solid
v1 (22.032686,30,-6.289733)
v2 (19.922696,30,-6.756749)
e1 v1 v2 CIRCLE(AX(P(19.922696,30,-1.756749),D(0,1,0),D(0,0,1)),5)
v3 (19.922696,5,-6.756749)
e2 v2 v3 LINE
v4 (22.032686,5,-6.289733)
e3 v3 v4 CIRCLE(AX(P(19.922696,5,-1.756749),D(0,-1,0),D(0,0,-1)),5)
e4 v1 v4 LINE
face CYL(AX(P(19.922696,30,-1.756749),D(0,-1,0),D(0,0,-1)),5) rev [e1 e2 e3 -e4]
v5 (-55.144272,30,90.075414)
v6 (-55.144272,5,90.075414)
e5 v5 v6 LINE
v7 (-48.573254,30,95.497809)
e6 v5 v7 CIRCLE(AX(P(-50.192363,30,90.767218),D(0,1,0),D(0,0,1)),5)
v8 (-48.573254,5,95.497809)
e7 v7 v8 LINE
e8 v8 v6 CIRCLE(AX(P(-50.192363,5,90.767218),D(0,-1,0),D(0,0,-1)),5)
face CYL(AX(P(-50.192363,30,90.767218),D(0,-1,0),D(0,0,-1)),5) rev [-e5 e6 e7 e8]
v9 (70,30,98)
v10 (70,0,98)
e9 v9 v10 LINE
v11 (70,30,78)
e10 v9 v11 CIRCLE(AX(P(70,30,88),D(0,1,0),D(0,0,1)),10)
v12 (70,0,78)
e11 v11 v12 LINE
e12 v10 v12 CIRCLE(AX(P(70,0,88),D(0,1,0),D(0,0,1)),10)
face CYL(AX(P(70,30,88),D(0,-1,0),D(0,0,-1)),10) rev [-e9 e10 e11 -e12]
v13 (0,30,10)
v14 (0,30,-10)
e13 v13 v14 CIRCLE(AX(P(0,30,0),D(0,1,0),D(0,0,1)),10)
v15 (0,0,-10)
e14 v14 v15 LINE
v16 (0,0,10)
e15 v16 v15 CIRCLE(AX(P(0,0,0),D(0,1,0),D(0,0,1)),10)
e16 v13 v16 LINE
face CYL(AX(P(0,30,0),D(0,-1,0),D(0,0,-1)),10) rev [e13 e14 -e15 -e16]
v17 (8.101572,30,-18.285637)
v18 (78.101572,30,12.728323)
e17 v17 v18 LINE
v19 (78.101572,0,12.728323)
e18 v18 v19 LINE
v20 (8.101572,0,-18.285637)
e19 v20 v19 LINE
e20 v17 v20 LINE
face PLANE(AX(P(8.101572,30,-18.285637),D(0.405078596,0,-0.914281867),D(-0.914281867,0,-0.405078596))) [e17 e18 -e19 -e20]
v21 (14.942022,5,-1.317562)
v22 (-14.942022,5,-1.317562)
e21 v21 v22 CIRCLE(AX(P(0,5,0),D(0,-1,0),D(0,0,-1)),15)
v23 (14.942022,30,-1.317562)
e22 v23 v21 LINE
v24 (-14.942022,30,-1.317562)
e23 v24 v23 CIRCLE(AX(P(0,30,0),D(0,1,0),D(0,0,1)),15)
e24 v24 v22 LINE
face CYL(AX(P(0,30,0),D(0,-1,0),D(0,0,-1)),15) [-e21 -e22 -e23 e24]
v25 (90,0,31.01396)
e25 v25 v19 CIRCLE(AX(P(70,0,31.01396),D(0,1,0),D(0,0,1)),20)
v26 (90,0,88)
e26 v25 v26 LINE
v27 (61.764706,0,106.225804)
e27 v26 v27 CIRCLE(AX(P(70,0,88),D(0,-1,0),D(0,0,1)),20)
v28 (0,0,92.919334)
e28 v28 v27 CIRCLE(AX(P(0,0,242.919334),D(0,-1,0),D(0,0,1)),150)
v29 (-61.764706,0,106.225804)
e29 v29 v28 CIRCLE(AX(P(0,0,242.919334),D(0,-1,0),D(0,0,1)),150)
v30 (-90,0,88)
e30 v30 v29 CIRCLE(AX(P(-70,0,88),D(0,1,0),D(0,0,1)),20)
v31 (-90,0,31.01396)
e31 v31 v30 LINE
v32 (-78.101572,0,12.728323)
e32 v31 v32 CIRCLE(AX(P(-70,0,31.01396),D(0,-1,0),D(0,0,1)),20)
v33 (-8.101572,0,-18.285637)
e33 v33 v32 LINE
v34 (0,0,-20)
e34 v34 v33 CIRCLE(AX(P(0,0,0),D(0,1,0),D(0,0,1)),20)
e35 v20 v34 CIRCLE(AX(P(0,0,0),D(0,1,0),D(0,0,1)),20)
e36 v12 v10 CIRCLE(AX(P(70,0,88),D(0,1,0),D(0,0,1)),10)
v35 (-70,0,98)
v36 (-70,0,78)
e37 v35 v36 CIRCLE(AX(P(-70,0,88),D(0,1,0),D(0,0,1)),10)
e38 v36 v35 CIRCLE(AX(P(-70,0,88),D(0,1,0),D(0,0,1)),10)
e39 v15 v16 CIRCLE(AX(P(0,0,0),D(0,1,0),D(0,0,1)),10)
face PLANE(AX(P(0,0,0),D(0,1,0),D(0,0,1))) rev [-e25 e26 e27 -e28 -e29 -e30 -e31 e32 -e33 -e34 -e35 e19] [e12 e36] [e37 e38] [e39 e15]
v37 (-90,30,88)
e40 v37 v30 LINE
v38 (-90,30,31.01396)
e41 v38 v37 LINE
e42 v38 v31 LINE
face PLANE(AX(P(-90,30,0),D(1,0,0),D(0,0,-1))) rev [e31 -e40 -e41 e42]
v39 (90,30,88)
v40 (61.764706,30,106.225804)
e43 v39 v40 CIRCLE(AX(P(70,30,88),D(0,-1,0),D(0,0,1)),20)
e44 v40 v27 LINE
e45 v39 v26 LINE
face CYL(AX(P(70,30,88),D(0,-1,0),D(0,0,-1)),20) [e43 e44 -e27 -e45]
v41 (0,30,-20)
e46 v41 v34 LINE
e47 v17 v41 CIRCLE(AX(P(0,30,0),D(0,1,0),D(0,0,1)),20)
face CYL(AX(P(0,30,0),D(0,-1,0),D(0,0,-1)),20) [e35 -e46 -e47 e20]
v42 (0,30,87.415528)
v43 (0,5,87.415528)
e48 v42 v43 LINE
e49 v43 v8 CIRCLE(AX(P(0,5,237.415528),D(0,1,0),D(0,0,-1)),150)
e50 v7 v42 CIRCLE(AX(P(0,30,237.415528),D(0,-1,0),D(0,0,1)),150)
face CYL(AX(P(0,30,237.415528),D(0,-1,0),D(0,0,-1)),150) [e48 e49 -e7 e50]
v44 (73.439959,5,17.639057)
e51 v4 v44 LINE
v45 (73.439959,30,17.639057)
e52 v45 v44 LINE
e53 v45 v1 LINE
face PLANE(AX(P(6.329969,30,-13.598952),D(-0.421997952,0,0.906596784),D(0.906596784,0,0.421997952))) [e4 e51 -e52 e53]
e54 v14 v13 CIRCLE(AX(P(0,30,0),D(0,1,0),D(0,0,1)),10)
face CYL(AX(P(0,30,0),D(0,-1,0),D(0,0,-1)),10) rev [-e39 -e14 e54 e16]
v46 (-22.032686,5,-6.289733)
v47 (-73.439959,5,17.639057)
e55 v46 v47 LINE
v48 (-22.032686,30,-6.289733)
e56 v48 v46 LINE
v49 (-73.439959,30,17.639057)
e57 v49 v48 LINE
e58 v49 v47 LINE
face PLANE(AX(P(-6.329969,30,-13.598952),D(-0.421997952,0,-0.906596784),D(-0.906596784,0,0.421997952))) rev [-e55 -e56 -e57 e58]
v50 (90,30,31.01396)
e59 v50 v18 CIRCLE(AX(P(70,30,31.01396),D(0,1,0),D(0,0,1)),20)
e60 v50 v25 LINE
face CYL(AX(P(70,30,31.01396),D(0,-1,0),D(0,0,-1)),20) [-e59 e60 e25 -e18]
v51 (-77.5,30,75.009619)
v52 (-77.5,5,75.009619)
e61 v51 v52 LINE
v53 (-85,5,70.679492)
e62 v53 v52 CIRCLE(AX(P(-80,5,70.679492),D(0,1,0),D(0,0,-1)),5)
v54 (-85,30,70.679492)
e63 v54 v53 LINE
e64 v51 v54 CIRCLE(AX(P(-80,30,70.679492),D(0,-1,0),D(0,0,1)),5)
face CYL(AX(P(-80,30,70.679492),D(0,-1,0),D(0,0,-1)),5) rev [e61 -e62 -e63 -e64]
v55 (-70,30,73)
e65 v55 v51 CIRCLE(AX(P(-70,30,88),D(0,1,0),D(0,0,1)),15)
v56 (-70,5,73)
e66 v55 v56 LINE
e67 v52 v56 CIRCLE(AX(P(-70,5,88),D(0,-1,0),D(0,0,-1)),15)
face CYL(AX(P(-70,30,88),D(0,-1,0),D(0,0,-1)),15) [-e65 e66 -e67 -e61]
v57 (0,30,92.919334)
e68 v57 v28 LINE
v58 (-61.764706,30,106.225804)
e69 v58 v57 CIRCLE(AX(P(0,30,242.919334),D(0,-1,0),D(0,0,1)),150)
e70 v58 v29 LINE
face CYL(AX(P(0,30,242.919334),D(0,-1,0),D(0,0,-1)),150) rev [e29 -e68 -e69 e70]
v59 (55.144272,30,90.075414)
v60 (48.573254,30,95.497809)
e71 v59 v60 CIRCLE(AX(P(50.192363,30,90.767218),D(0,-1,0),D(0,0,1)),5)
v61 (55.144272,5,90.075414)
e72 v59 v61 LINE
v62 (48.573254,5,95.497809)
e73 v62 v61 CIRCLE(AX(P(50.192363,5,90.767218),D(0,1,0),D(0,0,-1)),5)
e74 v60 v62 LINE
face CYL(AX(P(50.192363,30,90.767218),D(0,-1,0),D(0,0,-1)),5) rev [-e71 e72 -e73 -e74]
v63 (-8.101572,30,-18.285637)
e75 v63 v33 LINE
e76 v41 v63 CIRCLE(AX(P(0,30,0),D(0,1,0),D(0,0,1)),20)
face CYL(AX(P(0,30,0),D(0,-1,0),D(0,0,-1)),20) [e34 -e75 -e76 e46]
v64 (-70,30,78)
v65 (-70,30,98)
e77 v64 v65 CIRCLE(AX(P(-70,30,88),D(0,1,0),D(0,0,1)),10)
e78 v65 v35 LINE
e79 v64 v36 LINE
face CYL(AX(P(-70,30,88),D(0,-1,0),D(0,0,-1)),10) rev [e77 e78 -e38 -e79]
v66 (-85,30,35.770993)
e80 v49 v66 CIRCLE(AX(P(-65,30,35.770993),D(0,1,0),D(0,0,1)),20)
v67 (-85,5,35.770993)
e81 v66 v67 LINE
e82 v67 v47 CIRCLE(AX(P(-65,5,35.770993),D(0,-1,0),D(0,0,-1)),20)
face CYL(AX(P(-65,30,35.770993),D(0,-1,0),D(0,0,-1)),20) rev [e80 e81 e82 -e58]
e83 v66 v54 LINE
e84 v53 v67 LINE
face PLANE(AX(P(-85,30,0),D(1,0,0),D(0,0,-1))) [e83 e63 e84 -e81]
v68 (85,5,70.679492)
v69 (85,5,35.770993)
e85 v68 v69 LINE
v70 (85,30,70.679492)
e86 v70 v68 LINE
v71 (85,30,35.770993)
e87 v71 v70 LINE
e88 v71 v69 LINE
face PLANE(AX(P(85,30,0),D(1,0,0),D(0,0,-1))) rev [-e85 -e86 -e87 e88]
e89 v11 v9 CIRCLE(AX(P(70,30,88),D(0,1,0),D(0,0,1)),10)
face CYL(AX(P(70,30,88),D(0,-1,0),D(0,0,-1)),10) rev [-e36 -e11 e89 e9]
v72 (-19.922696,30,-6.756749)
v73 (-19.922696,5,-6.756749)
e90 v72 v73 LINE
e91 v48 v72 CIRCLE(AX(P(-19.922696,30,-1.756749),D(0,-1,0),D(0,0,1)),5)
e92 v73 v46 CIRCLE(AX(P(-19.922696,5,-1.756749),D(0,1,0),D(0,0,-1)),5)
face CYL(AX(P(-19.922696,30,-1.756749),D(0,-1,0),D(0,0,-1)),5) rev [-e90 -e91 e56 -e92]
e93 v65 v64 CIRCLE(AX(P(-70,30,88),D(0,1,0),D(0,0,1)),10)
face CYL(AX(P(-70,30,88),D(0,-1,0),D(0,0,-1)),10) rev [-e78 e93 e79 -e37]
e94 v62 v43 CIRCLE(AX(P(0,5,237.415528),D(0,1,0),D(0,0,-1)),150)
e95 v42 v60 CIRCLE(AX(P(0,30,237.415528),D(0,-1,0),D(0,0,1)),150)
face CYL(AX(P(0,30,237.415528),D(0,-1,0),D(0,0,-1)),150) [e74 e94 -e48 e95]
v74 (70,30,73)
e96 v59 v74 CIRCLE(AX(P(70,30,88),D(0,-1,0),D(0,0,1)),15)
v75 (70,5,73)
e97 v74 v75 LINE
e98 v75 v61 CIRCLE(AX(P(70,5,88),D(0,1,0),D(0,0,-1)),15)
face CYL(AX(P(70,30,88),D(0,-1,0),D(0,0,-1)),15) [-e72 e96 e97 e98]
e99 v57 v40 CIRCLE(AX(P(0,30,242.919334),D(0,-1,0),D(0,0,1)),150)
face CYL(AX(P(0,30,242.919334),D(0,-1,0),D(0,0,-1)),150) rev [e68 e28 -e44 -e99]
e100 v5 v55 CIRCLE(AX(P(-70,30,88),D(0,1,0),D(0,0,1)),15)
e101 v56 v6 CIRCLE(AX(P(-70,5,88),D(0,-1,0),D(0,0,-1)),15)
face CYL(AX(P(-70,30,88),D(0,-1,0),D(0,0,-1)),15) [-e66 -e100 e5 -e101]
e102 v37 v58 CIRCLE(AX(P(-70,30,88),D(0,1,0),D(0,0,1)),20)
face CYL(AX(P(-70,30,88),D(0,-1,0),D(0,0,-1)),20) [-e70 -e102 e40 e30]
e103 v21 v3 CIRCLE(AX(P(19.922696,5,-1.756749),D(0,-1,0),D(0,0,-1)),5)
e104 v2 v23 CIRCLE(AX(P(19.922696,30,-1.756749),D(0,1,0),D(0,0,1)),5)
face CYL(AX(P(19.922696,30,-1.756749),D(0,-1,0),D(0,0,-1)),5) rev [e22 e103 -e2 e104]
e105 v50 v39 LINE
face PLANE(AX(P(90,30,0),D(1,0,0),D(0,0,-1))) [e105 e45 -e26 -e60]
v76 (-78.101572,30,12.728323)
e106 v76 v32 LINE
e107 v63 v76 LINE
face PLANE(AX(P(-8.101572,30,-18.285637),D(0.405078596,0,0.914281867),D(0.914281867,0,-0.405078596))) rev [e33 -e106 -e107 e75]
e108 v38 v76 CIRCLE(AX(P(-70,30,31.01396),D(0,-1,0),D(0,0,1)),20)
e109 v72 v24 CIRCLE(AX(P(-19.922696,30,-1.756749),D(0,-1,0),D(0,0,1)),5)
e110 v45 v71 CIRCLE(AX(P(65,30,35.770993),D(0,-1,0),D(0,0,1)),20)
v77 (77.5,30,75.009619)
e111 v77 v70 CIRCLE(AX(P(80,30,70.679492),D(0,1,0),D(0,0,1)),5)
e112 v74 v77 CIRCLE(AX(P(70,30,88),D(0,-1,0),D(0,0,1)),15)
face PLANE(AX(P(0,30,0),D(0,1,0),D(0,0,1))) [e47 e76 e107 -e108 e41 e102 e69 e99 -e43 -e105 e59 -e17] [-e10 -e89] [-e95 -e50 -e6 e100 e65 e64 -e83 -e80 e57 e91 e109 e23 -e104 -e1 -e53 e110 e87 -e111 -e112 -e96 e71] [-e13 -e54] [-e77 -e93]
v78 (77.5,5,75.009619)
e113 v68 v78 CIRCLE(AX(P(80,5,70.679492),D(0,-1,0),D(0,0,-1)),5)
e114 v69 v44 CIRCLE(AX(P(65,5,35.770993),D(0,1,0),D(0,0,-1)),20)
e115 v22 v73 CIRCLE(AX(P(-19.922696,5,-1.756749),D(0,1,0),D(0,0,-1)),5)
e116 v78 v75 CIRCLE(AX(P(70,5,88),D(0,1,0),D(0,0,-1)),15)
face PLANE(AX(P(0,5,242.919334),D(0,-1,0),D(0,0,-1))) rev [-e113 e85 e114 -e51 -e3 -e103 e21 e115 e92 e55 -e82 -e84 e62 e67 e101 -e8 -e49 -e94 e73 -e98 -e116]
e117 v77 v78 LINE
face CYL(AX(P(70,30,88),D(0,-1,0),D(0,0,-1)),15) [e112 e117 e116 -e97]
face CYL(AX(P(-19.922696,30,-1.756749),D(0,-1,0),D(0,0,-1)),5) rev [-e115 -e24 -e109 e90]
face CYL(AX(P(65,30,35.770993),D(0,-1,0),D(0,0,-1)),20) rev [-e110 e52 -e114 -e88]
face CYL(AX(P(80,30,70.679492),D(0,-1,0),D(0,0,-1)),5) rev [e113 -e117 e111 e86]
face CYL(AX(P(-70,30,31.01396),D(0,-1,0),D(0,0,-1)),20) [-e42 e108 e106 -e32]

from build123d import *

# Parameters (mm, degrees)
PLATE_OUTLINE_SKETCH_R = 10
BASE_PLATE_DEPTH       = 30
POCKET_SKETCH_R        = 10
POCKET_DEPTH           = 5


with BuildPart() as part:
    # Plate Outline Sketch → Base Plate (new body)
    with BuildSketch(Plane(origin=(0, 0, 0), x_dir=(1, 0, 0), z_dir=(0, 1, 0))):
        with BuildLine():
            ThreePointArc((-90, -88), (-80.846522891, -104.803361008), (-61.764705882, -106.225803982))
            ThreePointArc((-61.764705882, -106.225803982), (0, -92.919333848), (61.764705882, -106.225803982))
            ThreePointArc((61.764705882, -106.225803982), (80.846522891, -104.803361008), (90, -88))
            Line((90, -88), (90, -31.013960492))
            ThreePointArc((90, -31.013960492), (86.763523469, -20.105968885), (78.101571911, -12.728323162))
            Line((78.101571911, -12.728323162), (8.101571911, 18.28563733))
            ThreePointArc((8.101571911, 18.28563733), (0, 20), (-8.101571911, 18.28563733))
            Line((-8.101571911, 18.28563733), (-78.101571911, -12.728323162))
            ThreePointArc((-78.101571911, -12.728323162), (-86.763523469, -20.105968885), (-90, -31.013960492))
            Line((-90, -31.013960492), (-90, -88))
        make_face()
        with Locations(Location((70, -88, 0), (0, 0, 270))):
            Circle(PLATE_OUTLINE_SKETCH_R, mode=Mode.SUBTRACT)
        with Locations(Location((-70, -88, 0), (0, 0, 270))):
            Circle(PLATE_OUTLINE_SKETCH_R, mode=Mode.SUBTRACT)
        with Locations(Location((0, 0, 0), (0, 0, 270))):
            Circle(PLATE_OUTLINE_SKETCH_R, mode=Mode.SUBTRACT)
        with BuildLine():
            ThreePointArc((55.144271878, -90.075413685), (61.617206501, -75.560997904), (77.5, -75.009618943))
            ThreePointArc((77.5, -75.009618943), (82.5, -75.009618943), (85, -70.679491924))
            Line((85, -70.679491924), (85, -35.770992672))
            ThreePointArc((85, -35.770992672), (81.864151045, -25.019229582), (73.439959048, -17.639056998))
            Line((73.439959048, -17.639056998), (22.032686199, 6.289732813))
            ThreePointArc((22.032686199, 6.289732813), (17.05201209, 5.850545589), (14.942022328, 1.317561671))
            ThreePointArc((14.942022328, 1.317561671), (0, -15), (-14.942022328, 1.317561671))
            ThreePointArc((-14.942022328, 1.317561671), (-17.05201209, 5.850545589), (-22.032686199, 6.289732813))
            Line((-22.032686199, 6.289732813), (-73.439959048, -17.639056998))
            ThreePointArc((-73.439959048, -17.639056998), (-81.864151045, -25.019229582), (-85, -35.770992672))
            Line((-85, -35.770992672), (-85, -70.679491924))
            ThreePointArc((-85, -70.679491924), (-82.5, -75.009618943), (-77.5, -75.009618943))
            ThreePointArc((-77.5, -75.009618943), (-61.617206501, -75.560997904), (-55.144271878, -90.075413685))
            ThreePointArc((-55.144271878, -90.075413685), (-53.374733144, -94.623708504), (-48.573254036, -95.497808883))
            ThreePointArc((-48.573254036, -95.497808883), (0, -87.415527975), (48.573254036, -95.497808883))
            ThreePointArc((48.573254036, -95.497808883), (53.374733144, -94.623708504), (55.144271878, -90.075413685))
        make_face(mode=Mode.SUBTRACT)
    extrude(amount=BASE_PLATE_DEPTH)

    # Pocket Sketch → Pocket (add)
    with BuildSketch(Plane.XZ):
        with BuildLine():
            Line((-90, 88), (-90, 31.013960492))
            ThreePointArc((-90, 31.013960492), (-86.763523469, 20.105968885), (-78.101571911, 12.728323162))
            Line((-78.101571911, 12.728323162), (-8.101571911, -18.28563733))
            ThreePointArc((-8.101571911, -18.28563733), (0, -20), (8.101571911, -18.28563733))
            Line((8.101571911, -18.28563733), (78.101571911, 12.728323162))
            ThreePointArc((78.101571911, 12.728323162), (86.763523469, 20.105968885), (90, 31.013960492))
            Line((90, 31.013960492), (90, 88))
            ThreePointArc((90, 88), (80.846522891, 104.803361008), (61.764705882, 106.225803982))
            ThreePointArc((61.764705882, 106.225803982), (0, 92.919333848), (-61.764705882, 106.225803982))
            ThreePointArc((-61.764705882, 106.225803982), (-80.846522891, 104.803361008), (-90, 88))
        make_face()
        with Locations(Location((-70, 88, 0), (0, 0, 90))):
            Circle(POCKET_SKETCH_R, mode=Mode.SUBTRACT)
        with Locations(Location((0, 0, 0), (0, 0, 90))):
            Circle(POCKET_SKETCH_R, mode=Mode.SUBTRACT)
        with Locations(Location((70, 88, 0), (0, 0, 90))):
            Circle(POCKET_SKETCH_R, mode=Mode.SUBTRACT)
    extrude(amount=-POCKET_DEPTH)


solid = part.part
